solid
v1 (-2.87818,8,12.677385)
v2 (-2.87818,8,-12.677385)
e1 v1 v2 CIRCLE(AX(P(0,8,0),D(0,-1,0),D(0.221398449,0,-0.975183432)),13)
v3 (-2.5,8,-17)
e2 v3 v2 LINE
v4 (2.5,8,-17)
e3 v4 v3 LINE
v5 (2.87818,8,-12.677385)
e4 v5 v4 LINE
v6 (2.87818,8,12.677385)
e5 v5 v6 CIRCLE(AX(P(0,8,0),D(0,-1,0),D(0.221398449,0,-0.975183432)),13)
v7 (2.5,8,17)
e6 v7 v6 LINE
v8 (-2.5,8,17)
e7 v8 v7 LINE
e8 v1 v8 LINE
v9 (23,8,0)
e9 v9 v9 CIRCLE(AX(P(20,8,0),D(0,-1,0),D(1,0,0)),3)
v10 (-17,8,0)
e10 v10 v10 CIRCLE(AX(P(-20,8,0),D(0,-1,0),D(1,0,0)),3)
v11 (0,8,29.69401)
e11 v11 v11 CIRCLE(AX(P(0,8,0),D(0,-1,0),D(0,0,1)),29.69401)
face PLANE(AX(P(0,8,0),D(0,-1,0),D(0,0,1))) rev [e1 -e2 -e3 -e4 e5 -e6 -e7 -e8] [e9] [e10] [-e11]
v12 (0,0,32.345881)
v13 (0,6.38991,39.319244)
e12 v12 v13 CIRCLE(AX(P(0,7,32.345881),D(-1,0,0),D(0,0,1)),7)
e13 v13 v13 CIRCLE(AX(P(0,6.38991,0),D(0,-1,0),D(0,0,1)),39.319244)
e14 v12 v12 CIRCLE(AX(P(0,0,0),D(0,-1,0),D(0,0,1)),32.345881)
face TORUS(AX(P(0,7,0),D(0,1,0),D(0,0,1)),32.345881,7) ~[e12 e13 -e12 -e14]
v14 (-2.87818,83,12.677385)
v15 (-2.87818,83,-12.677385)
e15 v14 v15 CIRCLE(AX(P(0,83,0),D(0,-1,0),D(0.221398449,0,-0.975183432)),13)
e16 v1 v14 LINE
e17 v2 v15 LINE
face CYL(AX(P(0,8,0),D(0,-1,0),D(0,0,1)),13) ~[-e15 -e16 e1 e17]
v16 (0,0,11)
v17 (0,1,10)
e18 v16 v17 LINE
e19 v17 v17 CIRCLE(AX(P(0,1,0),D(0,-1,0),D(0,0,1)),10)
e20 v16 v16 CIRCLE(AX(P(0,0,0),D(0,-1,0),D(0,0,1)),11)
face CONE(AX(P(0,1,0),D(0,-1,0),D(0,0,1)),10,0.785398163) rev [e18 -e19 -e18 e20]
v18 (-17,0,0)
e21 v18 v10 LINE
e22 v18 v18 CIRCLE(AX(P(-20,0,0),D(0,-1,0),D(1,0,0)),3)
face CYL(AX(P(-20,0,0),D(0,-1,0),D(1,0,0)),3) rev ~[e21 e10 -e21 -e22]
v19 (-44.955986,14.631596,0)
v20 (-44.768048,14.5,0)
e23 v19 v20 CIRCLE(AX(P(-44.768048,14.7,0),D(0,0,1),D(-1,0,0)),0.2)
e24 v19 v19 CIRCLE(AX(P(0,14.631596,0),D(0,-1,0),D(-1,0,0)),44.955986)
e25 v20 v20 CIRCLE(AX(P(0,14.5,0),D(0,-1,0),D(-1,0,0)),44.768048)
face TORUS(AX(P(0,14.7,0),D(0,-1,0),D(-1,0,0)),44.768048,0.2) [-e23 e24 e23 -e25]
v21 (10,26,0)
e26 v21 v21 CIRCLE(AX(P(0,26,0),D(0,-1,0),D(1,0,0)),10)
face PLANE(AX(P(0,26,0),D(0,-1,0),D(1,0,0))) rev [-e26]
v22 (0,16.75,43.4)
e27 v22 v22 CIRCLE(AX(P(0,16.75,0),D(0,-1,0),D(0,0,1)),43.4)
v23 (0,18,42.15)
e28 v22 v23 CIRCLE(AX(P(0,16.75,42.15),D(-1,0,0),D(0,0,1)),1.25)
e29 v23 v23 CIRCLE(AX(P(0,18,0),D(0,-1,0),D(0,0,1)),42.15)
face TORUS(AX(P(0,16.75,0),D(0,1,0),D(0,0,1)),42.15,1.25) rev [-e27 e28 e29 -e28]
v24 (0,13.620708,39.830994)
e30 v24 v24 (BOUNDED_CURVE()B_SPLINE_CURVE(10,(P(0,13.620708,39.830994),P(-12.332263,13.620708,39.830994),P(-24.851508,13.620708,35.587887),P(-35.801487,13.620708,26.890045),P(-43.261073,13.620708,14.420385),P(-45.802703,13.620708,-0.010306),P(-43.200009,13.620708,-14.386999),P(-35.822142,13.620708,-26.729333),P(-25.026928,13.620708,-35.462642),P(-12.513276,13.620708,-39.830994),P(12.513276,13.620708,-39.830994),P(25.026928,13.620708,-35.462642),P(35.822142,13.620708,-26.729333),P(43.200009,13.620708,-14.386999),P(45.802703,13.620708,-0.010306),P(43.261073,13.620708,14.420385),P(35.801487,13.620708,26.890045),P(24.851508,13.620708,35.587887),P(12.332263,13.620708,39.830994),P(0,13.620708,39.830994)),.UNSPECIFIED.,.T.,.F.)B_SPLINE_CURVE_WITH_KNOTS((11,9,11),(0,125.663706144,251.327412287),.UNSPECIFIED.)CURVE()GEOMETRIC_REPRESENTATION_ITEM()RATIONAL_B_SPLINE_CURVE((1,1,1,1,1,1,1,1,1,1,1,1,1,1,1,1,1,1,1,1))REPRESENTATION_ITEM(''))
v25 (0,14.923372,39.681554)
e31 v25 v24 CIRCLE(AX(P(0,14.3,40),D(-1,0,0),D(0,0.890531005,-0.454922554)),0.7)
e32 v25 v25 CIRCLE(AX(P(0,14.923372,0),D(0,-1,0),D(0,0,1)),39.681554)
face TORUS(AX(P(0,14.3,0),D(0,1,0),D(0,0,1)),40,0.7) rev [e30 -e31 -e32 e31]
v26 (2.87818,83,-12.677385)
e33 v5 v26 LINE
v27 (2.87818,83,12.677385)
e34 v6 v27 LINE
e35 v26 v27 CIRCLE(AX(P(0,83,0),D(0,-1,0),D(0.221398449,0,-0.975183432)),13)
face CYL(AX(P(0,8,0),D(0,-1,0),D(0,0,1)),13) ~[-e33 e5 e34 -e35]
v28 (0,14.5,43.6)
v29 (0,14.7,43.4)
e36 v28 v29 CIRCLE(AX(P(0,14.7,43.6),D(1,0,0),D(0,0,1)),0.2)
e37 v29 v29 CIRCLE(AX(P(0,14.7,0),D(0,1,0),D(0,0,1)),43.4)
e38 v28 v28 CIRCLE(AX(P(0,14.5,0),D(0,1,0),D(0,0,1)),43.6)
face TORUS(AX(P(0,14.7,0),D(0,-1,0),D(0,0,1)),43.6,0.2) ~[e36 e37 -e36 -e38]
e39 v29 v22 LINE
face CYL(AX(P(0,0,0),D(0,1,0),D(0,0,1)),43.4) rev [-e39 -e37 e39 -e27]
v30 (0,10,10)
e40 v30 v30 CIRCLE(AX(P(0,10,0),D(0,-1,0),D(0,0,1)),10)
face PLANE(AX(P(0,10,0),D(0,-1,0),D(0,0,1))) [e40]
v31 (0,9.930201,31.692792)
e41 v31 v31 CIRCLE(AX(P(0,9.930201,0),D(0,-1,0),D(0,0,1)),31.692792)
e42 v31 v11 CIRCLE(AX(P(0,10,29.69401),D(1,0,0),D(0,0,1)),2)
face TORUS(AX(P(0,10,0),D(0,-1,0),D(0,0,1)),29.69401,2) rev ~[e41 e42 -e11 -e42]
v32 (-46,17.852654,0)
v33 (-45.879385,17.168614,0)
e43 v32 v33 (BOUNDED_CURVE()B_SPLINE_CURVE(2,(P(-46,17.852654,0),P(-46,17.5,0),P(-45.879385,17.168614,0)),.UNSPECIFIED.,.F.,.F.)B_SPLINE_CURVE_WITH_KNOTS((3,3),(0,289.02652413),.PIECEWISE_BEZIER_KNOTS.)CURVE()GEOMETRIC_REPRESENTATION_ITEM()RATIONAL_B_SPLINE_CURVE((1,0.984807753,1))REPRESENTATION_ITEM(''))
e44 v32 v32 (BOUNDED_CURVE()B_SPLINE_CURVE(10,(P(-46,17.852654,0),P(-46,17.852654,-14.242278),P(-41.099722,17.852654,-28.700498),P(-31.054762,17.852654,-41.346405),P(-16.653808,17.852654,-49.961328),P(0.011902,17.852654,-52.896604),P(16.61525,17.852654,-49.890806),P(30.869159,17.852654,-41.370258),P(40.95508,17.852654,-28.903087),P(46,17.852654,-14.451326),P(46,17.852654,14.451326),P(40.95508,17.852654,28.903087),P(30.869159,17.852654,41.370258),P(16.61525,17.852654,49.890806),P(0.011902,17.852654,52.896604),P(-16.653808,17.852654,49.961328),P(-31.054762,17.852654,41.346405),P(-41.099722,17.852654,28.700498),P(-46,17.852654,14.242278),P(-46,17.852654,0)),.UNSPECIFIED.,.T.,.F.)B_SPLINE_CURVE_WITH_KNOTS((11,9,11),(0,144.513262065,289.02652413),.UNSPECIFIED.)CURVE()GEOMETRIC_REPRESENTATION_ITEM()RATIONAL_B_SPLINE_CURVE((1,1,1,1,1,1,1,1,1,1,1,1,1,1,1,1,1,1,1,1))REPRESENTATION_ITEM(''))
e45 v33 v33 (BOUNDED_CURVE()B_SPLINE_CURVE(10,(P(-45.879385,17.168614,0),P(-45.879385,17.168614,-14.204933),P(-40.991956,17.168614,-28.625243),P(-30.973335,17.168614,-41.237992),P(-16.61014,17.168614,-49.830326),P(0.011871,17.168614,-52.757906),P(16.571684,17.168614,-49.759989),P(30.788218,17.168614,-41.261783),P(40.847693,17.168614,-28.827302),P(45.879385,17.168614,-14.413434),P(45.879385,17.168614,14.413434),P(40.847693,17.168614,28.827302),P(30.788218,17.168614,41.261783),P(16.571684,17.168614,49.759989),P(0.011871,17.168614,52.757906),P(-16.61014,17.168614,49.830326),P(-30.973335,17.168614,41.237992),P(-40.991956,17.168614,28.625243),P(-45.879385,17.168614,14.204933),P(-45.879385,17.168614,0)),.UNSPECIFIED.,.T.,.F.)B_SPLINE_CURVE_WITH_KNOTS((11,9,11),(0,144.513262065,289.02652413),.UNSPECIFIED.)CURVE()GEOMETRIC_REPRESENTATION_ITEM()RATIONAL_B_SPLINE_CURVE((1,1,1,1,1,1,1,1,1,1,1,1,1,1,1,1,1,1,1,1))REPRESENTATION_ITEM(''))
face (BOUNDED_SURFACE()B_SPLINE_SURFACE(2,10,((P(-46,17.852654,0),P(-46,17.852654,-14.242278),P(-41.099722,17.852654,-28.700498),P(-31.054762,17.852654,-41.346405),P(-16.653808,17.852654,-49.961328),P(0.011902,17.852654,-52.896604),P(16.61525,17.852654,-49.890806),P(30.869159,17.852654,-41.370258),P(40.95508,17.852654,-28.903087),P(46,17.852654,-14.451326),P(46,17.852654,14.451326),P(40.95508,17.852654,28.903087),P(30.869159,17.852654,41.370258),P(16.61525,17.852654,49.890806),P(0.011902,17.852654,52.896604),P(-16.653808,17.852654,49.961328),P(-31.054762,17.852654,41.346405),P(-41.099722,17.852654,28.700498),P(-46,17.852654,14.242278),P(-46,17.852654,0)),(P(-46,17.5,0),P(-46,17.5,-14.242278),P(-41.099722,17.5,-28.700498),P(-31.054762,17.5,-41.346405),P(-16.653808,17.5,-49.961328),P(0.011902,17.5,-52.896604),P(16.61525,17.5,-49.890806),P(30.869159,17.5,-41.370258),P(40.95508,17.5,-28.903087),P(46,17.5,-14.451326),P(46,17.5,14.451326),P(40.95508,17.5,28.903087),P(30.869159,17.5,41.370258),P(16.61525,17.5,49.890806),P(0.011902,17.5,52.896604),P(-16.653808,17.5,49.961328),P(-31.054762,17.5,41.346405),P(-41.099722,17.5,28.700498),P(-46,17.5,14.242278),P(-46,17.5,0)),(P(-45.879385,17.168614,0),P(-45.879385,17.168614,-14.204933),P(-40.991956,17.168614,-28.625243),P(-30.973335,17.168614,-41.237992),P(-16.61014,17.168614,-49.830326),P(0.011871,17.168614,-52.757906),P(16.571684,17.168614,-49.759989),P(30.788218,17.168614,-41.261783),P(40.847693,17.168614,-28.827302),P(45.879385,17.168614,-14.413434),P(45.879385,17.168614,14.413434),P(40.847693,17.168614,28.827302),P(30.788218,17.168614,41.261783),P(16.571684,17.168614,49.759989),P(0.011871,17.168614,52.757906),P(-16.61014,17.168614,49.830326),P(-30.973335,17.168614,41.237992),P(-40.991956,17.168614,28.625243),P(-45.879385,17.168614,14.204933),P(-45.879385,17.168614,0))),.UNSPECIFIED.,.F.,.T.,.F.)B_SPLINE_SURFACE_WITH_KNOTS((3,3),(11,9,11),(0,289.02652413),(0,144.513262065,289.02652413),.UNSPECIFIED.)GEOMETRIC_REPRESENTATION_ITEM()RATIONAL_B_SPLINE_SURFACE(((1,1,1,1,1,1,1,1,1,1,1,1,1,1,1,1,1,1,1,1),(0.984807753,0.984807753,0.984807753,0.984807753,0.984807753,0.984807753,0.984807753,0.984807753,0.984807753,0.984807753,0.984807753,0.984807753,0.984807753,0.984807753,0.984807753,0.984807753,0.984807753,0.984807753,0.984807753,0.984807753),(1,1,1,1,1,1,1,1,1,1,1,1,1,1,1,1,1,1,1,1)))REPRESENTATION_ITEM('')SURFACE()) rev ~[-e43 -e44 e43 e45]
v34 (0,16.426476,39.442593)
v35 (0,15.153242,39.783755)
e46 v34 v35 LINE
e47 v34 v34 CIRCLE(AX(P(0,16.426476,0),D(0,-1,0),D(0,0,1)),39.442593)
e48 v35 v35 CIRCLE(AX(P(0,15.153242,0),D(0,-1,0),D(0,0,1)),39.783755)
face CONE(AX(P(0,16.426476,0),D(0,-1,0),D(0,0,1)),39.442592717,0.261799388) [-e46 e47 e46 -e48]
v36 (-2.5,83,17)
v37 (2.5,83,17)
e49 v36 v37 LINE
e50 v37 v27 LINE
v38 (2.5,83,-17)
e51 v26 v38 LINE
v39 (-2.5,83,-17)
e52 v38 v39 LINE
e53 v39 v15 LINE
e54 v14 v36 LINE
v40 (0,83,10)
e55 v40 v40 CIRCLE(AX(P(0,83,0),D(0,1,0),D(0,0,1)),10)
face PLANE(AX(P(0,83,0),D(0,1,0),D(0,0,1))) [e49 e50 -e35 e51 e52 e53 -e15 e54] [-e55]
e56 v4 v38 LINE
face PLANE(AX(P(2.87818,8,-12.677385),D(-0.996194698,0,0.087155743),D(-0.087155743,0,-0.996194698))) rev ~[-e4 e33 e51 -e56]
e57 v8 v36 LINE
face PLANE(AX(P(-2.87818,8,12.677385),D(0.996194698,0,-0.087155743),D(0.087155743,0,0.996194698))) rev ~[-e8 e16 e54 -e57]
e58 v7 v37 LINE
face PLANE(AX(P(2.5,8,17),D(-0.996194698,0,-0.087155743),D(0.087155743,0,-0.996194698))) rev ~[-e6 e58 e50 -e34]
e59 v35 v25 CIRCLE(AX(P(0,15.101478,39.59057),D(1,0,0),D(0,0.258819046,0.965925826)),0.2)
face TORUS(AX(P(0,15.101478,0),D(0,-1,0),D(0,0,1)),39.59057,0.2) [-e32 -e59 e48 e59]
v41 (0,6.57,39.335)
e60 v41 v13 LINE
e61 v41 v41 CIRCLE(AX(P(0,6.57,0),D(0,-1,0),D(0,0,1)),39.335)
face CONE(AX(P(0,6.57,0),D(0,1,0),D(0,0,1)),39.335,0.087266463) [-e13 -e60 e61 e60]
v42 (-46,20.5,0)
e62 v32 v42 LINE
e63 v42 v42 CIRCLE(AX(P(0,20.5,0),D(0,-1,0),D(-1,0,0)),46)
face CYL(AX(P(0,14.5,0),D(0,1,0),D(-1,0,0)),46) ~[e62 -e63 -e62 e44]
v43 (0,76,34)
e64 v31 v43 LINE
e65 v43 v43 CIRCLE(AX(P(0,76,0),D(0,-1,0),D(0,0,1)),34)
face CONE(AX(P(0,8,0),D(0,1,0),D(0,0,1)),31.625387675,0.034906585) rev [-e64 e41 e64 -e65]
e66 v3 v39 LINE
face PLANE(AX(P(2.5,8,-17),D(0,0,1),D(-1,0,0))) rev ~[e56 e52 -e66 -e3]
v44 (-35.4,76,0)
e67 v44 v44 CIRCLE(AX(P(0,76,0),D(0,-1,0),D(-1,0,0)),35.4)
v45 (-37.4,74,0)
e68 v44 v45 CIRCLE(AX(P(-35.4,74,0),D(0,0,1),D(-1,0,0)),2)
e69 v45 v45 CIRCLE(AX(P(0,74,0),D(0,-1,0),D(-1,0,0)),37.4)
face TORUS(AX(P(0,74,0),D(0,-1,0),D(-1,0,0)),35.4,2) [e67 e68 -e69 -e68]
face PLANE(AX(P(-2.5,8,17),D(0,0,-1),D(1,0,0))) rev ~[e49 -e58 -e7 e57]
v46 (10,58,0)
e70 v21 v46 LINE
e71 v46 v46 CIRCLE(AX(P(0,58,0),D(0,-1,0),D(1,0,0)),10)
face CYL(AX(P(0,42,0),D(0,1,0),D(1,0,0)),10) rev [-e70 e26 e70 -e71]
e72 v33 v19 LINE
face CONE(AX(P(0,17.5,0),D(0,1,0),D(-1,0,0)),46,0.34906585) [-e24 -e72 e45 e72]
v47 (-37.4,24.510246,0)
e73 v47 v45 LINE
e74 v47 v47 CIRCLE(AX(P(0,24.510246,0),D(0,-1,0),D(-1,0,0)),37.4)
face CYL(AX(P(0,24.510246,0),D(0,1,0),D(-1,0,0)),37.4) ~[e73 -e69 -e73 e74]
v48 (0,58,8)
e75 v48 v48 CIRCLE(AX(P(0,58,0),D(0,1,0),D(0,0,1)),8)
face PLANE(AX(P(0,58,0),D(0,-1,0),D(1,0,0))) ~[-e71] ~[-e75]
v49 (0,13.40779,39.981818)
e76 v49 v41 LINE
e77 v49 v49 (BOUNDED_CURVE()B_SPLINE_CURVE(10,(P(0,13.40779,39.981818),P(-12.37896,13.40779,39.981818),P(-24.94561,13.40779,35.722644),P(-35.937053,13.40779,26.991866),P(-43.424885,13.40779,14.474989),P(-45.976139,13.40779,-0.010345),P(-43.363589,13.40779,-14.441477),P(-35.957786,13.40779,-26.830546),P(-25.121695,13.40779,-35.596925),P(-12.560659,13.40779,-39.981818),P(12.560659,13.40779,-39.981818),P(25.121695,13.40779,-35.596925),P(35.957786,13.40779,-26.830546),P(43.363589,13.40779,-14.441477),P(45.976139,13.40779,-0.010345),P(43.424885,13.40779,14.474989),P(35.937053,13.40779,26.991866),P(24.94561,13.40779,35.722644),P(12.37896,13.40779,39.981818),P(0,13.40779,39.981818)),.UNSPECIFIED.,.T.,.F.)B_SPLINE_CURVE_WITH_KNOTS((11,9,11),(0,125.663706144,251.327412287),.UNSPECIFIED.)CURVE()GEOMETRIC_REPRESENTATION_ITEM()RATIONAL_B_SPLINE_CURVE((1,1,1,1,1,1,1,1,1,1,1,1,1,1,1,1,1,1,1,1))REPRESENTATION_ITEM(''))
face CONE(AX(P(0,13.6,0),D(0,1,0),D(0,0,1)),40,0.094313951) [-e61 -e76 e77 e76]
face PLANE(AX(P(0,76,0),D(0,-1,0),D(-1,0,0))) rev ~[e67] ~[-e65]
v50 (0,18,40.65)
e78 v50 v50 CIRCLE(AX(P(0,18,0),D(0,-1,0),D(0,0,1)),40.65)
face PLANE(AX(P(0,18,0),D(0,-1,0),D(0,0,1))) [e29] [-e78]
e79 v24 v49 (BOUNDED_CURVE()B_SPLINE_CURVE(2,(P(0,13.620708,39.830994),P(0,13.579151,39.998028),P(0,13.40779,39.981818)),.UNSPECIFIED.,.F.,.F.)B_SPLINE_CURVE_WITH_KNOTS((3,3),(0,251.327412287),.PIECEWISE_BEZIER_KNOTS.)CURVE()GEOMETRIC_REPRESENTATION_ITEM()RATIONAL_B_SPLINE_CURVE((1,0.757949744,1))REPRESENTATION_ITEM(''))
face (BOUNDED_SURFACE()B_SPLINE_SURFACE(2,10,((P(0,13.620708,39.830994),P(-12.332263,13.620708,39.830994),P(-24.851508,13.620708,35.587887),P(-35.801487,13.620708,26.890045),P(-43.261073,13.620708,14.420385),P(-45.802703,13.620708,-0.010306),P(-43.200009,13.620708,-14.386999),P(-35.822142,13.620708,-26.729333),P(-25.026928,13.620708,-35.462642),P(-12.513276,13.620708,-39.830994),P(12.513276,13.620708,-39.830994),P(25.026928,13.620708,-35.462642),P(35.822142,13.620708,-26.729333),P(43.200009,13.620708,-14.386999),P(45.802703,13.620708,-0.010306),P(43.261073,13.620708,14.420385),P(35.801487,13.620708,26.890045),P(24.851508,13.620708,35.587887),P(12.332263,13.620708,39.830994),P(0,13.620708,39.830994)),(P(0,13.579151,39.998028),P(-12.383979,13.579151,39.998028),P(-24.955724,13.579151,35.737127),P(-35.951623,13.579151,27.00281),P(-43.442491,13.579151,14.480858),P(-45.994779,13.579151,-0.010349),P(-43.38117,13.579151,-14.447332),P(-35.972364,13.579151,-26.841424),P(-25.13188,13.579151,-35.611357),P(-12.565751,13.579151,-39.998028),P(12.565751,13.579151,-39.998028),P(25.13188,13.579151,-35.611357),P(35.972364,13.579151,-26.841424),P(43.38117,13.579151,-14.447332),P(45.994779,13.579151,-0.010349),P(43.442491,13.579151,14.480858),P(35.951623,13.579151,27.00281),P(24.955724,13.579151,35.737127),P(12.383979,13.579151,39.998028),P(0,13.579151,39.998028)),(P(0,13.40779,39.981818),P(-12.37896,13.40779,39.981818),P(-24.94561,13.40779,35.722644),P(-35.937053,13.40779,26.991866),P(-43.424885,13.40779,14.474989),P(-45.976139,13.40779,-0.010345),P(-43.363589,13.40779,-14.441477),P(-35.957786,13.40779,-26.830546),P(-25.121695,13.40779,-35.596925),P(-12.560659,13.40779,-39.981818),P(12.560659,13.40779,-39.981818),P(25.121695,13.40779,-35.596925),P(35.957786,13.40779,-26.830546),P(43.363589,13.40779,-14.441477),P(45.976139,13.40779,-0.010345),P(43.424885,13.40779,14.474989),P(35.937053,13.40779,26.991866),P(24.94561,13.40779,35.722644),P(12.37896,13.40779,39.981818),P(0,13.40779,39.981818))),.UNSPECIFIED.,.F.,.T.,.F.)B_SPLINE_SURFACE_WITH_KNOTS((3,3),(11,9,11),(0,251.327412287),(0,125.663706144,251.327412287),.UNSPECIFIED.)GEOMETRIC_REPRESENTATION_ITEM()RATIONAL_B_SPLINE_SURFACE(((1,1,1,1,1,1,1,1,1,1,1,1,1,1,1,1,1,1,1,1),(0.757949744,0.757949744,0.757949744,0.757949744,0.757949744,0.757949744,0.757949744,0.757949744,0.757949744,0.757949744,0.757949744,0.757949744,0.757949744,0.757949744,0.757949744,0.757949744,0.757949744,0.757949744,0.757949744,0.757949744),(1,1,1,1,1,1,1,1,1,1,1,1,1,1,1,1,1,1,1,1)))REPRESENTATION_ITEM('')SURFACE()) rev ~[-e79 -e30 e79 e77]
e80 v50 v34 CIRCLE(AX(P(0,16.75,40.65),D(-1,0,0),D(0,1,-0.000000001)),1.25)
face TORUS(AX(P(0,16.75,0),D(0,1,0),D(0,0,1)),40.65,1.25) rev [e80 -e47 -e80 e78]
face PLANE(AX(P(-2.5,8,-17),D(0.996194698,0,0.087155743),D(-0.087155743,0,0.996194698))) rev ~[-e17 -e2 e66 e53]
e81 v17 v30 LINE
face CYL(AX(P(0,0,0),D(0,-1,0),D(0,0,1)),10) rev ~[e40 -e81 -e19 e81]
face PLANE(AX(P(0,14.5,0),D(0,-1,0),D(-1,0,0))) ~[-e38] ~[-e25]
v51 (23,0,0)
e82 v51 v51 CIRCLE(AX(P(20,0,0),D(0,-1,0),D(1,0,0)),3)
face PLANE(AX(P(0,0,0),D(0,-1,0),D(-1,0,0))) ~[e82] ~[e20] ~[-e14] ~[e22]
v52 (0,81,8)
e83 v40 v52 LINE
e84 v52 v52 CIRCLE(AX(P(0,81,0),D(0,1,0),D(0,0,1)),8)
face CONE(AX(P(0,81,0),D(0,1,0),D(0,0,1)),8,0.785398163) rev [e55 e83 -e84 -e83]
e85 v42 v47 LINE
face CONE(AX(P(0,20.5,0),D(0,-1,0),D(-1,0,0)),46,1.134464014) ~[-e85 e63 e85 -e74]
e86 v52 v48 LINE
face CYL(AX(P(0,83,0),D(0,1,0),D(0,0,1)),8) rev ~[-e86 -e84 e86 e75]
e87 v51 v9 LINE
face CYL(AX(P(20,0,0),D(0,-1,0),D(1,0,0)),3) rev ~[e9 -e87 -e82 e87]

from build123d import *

# Parameters (mm, degrees)
CHAMFER1_SIZE       = 3
CHAMFER1_SIZE2      = 1.091910703
SKETCH4_R           = 13
BOSS_EXTRUDE1_DEPTH = 75
BOSS_EXTRUDE2_DEPTH = 75
CIRPATTERN1_COUNT   = 2
FILLET1_R           = 2
FILLET2_R           = 2
SKETCH6_W           = 10
SKETCH6_H           = 32
SKETCH7_R           = 8
CUT_EXTRUDE1_DEPTH  = 30
SKETCH8_R           = 3
CUT_EXTRUDE2_DEPTH  = 30
CHAMFER2_SIZE       = 2
SKETCH9_R           = 10
CUT_EXTRUDE3_DEPTH  = 10
CHAMFER3_SIZE       = 1
FILLET3_R           = 7
FILLET4_R           = 2
FILLET5_R           = 0.2
FILLET6_R           = 1.25
FILLET7_R           = 0.2


with BuildPart() as part:
    # Sketch2 → Revolve1 (revolve)
    with BuildSketch(Plane.XY, mode=Mode.PRIVATE) as revolve1_sk:
        Polygon((0, 0), (40, 0), (40, 14.5), (46, 14.5), (46, 20.5), (37.4, 24.51024586), (37.4, 76), (0, 76), align=None)
    revolve(revolve1_sk.sketch.rotate(Axis((0, 76, 0), (0, -1, 0)), 180), axis=Axis((0, 76, 0), (0, -1, 0)))

    # Chamfer1
    chamfer1_edges = [part.edges().sort_by_distance(p)[0] for p in [
        (46, 14.5, 0),
    ]]
    chamfer1_side = [part.faces().sort_by_distance(p)[0] for p in [
        (46, 17.5, 0),
    ]]
    chamfer(chamfer1_edges, length=CHAMFER1_SIZE, length2=CHAMFER1_SIZE2, reference=chamfer1_side[0])

    # Sketch3 → Cut-Revolve1 (revolve, cut)
    with BuildSketch(Plane.XY, mode=Mode.PRIVATE) as cut_revolve1_sk:
        Polygon((34, 76), (0, 76), (0, 8), (31.625387675, 8), align=None)
    revolve(cut_revolve1_sk.sketch.rotate(Axis((0, 134.916718262, 0), (0, -1, 0)), 90), axis=Axis((0, 134.916718262, 0), (0, -1, 0)), mode=Mode.SUBTRACT)

    # Sketch4 → Boss-Extrude1 (add)
    with BuildSketch(Plane(origin=(0, 8, 0), x_dir=(1, 0, 0), z_dir=(0, 1, 0))):
        with Locations(Location((0, 0, 0), (0, 0, 270))):
            Circle(SKETCH4_R)
    extrude(amount=BOSS_EXTRUDE1_DEPTH)

    # Sketch5 → Boss-Extrude2 (add)
    with BuildSketch(Plane(origin=(0, 8, 0), x_dir=(1, 0, 0), z_dir=(0, 1, 0))):
        with BuildLine():
            Line((-2.5, 17), (-2.878179843, 12.67738462))
            ThreePointArc((-2.878179843, 12.67738462), (0, 13), (2.878179843, 12.67738462))
            Line((2.878179843, 12.67738462), (2.5, 17))
            Line((2.5, 17), (-2.5, 17))
        make_face()
    boss_extrude2 = extrude(amount=BOSS_EXTRUDE2_DEPTH)

    # CirPattern1: Boss-Extrude2 ×2 about axis
    cirpattern1_axis = Axis((0, 0, 0), (0, 1, 0))
    for i in range(1, CIRPATTERN1_COUNT):
        add(boss_extrude2.rotate(cirpattern1_axis, i * 360 / CIRPATTERN1_COUNT))

    # Fillet1
    fillet1_edges = [part.edges().sort_by_distance(p)[0] for p in [
        (0, 8, -31.625387675),
    ]]
    fillet(fillet1_edges, radius=FILLET1_R)

    # Fillet2
    fillet2_edges = [part.edges().sort_by_distance(p)[0] for p in [
        (37.4, 76, 0),
    ]]
    fillet(fillet2_edges, radius=FILLET2_R)

    # Sketch6 → Cut-Revolve2 (revolve, cut)
    with BuildSketch(Plane(origin=(0, 0, 0), x_dir=(0, 0, -1), z_dir=(1, 0, 0)), mode=Mode.PRIVATE) as cut_revolve2_sk:
        with Locations((5, 42)):
            Rectangle(SKETCH6_W, SKETCH6_H)
    revolve(cut_revolve2_sk.sketch.rotate(Axis((0, 140.488845923, 0), (0, -1, 0)), 90), axis=Axis((0, 140.488845923, 0), (0, -1, 0)), mode=Mode.SUBTRACT)

    # Sketch7 → Cut-Extrude1 (cut)
    with BuildSketch(Plane(origin=(0, 83, 0), x_dir=(1, 0, 0), z_dir=(0, 1, 0))):
        with Locations(Location((0, 0, 0), (0, 0, 270))):
            Circle(SKETCH7_R)
    extrude(amount=-CUT_EXTRUDE1_DEPTH, mode=Mode.SUBTRACT)

    # Sketch8 → Cut-Extrude2 (cut)
    with BuildSketch(Plane.XZ):
        with Locations((-20, 0)):
            Circle(SKETCH8_R)
        with Locations((20, 0)):
            Circle(SKETCH8_R)
    extrude(amount=-CUT_EXTRUDE2_DEPTH, mode=Mode.SUBTRACT)

    # Chamfer2
    chamfer2_edges = [part.edges().sort_by_distance(p)[0] for p in [
        (0, 83, -8),
    ]]
    chamfer(chamfer2_edges, length=CHAMFER2_SIZE)

    # Sketch9 → Cut-Extrude3 (cut)
    with BuildSketch(Plane.XZ):
        with Locations(Location((0, 0, 0), (0, 0, 90))):
            Circle(SKETCH9_R)
    extrude(amount=-CUT_EXTRUDE3_DEPTH, mode=Mode.SUBTRACT)

    # Chamfer3
    chamfer3_edges = [part.edges().sort_by_distance(p)[0] for p in [
        (0, 0, -10),
    ]]
    chamfer(chamfer3_edges, length=CHAMFER3_SIZE)

    # Sketch10 → Cut-Revolve3 (revolve, cut)
    with BuildSketch(Plane.XY, mode=Mode.PRIVATE) as cut_revolve3_sk:
        with BuildLine():
            Line((-43.4, 14.5), (-43.4, 18))
            Line((-43.4, 18), (-40.65, 18))
            ThreePointArc((-40.65, 18), (-39.658308325, 17.510951786), (-39.442592717, 16.426476194))
            Line((-39.442592717, 16.426476194), (-39.783754868, 15.153241714))
            ThreePointArc((-39.783754868, 15.153241714), (-39.773321328, 15.020226176), (-39.681554213, 14.923371704))
            ThreePointArc((-39.681554213, 14.923371704), (-39.319426642, 14.136232165), (-40, 13.6))
            Line((-40, 13.6), (-39.335, 6.57))
            Line((-39.335, 6.57), (-38.760199481, 0))
            Line((-38.760199481, 0), (-43.4, 0))
            Line((-43.4, 0), (-43.4, 14.5))
        make_face()
    revolve(cut_revolve3_sk.sketch.rotate(Axis((0, 143.968242968, 0), (0, -1, 0)), 270), axis=Axis((0, 143.968242968, 0), (0, -1, 0)), mode=Mode.SUBTRACT)

    # Fillet3
    fillet3_edges = [part.edges().sort_by_distance(p)[0] for p in [
        (0, 0, -38.760199481),
    ]]
    fillet(fillet3_edges, radius=FILLET3_R)

    # Fillet4
    fillet4_edges = [part.edges().sort_by_distance(p)[0] for p in [
        (46, 17.5, 0),
    ]]
    fillet(fillet4_edges, radius=FILLET4_R)

    # Fillet5
    fillet5_edges = [part.edges().sort_by_distance(p)[0] for p in [
        (0, 14.5, -43.4),
        (44.908089297, 14.5, 0),
    ]]
    fillet(fillet5_edges, radius=FILLET5_R)

    # Fillet6
    fillet6_edges = [part.edges().sort_by_distance(p)[0] for p in [
        (0, 18, -43.4),
    ]]
    fillet(fillet6_edges, radius=FILLET6_R)

    # Fillet7
    fillet7_edges = [part.edges().sort_by_distance(p)[0] for p in [
        (0, 13.6, -40),
    ]]
    fillet(fillet7_edges, radius=FILLET7_R)


solid = part.part
